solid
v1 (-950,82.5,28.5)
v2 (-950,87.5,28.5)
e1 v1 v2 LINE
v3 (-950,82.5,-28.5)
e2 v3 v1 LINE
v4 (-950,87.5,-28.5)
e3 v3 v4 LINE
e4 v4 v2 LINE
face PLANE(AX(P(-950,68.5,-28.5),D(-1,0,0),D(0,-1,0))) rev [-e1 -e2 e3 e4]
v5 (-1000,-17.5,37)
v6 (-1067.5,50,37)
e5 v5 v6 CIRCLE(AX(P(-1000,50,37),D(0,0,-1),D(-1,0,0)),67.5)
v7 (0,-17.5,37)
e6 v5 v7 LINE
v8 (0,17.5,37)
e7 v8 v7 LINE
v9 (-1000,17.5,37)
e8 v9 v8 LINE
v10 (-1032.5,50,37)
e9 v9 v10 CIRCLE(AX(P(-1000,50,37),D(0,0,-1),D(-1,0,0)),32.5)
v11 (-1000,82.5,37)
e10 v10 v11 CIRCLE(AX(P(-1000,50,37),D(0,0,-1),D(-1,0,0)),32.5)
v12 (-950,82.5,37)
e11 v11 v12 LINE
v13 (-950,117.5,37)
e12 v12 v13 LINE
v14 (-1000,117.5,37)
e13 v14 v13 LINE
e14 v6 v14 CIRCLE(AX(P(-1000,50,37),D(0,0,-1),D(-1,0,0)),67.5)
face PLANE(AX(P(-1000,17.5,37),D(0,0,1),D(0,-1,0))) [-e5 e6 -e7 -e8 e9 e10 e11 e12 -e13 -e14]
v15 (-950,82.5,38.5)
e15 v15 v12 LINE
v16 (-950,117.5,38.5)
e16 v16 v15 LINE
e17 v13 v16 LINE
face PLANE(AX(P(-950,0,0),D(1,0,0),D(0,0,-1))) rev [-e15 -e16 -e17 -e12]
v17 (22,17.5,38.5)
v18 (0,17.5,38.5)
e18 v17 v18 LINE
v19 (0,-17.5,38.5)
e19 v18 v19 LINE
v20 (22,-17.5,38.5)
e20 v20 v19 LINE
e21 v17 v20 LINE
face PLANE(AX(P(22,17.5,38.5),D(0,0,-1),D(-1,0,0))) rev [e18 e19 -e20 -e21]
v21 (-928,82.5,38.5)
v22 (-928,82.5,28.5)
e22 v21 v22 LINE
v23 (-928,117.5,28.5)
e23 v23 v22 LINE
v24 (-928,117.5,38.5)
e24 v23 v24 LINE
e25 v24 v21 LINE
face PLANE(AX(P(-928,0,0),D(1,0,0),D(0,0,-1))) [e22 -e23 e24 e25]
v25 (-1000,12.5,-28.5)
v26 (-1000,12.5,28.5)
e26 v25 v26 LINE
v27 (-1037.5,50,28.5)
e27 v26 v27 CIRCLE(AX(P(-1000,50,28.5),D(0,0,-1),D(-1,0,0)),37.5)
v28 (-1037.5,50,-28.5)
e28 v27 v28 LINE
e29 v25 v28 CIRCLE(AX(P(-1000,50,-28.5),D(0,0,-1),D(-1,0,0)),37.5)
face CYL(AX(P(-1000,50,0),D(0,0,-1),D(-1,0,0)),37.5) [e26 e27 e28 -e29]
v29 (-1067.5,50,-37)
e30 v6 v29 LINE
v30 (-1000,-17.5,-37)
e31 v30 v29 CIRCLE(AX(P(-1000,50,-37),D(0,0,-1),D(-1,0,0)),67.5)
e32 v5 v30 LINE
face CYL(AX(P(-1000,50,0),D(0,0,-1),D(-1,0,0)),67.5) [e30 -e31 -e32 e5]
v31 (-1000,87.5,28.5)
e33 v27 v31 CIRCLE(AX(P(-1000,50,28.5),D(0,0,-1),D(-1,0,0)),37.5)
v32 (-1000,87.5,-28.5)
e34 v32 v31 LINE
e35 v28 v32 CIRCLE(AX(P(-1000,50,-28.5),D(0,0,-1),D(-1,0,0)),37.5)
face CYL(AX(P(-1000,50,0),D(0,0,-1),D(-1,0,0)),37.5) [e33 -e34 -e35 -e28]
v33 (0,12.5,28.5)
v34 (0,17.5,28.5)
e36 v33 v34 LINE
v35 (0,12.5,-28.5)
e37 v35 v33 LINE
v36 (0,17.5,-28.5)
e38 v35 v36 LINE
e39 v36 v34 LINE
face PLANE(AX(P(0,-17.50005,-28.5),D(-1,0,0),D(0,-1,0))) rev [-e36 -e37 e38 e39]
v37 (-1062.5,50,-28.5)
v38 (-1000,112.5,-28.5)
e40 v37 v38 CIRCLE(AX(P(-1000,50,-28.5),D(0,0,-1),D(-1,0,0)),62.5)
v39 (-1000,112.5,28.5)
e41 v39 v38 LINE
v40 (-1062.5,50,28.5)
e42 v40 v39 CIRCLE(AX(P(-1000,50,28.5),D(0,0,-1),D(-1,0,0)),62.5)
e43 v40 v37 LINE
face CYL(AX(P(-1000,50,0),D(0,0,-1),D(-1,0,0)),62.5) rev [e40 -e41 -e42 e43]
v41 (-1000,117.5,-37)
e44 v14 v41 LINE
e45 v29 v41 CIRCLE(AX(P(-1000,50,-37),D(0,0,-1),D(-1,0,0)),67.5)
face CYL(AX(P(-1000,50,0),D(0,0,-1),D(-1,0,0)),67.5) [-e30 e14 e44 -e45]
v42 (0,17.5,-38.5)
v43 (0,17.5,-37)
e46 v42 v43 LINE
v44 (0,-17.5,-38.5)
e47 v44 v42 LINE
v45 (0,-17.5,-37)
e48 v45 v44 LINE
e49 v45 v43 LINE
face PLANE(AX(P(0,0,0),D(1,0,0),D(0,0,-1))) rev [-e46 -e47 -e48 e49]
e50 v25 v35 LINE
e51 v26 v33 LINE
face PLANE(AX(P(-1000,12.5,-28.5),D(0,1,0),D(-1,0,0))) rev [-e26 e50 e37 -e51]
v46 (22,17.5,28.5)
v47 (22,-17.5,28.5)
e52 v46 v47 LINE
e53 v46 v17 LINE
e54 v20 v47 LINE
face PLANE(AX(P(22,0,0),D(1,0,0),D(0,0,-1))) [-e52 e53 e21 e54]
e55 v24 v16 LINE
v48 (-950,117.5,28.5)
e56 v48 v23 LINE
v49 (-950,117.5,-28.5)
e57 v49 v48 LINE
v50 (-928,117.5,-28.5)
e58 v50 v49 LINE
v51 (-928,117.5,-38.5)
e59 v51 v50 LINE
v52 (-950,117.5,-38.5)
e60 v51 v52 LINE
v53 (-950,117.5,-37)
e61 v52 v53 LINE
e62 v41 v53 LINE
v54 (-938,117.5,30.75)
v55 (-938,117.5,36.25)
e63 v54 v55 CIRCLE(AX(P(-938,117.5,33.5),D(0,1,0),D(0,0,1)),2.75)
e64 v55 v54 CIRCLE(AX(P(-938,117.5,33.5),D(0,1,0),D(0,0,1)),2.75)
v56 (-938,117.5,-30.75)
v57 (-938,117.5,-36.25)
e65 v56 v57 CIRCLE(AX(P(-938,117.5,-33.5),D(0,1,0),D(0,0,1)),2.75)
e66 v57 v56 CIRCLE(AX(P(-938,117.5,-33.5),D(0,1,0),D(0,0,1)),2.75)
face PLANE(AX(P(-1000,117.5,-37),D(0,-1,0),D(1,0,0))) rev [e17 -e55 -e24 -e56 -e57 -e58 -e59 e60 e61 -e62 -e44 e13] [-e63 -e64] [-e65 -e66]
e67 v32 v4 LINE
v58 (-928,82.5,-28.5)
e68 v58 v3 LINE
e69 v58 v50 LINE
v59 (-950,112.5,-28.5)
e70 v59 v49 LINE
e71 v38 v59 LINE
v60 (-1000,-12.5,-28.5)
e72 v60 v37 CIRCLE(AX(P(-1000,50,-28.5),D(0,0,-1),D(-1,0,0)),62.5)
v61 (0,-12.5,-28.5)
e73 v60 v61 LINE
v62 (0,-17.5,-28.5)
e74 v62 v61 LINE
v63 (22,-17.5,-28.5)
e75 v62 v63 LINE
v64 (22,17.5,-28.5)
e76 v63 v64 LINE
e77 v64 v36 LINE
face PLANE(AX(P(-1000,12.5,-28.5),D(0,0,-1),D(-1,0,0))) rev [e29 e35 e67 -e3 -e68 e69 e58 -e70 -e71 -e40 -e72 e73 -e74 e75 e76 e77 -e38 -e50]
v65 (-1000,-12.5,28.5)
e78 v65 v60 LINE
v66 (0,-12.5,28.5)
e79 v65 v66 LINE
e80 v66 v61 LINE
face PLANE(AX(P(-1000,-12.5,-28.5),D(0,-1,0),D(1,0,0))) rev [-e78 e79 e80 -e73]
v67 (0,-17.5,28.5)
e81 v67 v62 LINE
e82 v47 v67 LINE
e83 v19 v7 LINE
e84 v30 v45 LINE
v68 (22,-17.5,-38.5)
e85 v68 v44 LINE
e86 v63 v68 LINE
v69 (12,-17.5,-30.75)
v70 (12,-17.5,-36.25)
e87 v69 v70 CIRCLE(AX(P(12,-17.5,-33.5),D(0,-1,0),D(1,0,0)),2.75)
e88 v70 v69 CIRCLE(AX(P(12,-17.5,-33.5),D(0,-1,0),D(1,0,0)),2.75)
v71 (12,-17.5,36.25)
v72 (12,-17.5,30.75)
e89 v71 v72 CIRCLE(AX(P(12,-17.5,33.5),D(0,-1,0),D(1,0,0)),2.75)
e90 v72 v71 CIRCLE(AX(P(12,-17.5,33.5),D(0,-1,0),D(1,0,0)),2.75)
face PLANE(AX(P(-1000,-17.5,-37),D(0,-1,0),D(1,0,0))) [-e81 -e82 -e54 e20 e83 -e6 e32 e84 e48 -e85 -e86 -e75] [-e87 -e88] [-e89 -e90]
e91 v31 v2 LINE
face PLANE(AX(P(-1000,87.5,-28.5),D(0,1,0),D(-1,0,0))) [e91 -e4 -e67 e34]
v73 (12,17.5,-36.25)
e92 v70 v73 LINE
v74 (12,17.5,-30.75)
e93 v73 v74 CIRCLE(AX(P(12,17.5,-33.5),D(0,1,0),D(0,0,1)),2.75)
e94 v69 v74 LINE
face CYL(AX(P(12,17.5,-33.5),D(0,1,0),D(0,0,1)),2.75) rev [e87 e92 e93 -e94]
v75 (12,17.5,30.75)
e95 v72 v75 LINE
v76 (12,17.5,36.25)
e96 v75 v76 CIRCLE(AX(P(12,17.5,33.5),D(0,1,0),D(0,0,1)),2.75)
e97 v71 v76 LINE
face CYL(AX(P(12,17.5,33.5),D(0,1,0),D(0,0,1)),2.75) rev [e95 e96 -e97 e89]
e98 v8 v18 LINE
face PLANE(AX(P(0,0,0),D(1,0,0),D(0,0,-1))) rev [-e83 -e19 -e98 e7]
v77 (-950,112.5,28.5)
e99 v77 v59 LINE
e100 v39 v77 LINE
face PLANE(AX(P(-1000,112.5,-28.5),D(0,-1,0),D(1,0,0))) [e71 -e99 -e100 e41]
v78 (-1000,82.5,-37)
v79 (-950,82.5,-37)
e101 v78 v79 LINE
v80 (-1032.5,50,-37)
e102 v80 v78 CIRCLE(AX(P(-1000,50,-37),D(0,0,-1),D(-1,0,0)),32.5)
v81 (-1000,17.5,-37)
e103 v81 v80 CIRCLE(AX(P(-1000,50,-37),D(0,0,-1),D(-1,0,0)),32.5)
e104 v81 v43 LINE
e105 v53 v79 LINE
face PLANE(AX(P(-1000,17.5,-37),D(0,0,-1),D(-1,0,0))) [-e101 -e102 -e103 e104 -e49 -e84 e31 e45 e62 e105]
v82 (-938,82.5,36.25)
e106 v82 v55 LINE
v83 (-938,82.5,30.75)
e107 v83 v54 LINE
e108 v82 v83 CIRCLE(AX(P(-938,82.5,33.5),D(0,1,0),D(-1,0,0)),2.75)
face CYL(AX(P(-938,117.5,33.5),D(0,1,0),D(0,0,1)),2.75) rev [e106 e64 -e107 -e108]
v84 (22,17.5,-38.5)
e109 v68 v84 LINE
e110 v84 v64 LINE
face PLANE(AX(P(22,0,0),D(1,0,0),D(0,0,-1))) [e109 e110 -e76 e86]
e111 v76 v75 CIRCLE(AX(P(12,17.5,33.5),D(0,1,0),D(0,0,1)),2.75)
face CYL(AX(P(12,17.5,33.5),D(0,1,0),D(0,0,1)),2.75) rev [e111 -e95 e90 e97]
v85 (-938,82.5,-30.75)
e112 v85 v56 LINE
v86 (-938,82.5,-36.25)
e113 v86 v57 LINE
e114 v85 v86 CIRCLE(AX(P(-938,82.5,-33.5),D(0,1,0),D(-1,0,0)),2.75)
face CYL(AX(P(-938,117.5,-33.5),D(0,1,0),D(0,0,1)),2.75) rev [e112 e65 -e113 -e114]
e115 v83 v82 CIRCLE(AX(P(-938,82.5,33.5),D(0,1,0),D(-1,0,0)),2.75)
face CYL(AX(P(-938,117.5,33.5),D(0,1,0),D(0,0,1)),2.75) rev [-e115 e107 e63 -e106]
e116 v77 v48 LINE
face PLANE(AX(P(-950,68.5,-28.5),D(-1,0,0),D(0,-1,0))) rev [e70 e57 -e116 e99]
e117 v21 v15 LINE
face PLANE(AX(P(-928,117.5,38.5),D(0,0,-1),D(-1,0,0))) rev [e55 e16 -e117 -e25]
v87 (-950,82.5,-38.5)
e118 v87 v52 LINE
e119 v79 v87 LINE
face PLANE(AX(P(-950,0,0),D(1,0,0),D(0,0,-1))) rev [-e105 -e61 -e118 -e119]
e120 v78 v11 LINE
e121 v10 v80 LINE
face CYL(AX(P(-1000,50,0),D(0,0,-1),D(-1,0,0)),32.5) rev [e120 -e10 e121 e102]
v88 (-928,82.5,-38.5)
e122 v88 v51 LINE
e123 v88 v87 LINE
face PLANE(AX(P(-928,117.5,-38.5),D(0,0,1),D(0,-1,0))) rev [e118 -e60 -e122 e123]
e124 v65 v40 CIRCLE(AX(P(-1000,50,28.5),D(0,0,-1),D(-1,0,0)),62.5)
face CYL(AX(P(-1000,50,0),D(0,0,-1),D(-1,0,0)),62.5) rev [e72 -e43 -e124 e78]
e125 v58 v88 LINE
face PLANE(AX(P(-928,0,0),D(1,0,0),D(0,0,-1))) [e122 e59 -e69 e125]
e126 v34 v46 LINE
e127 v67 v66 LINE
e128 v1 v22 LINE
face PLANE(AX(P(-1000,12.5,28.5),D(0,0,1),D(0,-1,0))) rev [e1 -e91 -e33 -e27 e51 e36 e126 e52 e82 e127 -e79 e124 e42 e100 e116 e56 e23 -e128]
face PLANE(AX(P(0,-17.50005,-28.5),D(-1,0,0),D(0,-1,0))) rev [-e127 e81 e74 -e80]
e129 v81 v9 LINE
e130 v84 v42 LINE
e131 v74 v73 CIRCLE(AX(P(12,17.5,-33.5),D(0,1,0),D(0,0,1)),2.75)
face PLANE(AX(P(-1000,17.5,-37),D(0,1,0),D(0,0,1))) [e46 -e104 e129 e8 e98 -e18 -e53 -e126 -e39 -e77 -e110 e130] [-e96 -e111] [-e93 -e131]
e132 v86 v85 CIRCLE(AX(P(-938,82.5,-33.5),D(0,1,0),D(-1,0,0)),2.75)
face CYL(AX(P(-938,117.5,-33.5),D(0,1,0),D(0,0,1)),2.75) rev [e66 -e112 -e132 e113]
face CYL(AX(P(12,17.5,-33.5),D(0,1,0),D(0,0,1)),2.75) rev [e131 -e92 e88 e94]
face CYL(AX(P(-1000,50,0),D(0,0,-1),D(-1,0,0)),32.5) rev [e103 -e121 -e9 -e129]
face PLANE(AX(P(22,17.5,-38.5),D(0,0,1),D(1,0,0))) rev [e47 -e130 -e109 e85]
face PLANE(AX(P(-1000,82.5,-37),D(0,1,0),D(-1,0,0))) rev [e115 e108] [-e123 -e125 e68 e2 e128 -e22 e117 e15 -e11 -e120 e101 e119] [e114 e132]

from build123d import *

# Parameters (mm, degrees)
SKETCH_2_W                  = 74
SKETCH_2_H                  = 35
SKETCH_2_W_2                = 57
SKETCH_2_H_2                = 25
SKETCH_11_W                 = 77
SKETCH_11_H                 = 35
SKETCH_11_W_2               = 57
SKETCH_11_H_2               = 25
EXTRUDE_1_DEPTH             = 22
SKETCH_12_W                 = 23.011901601
SKETCH_12_H                 = 57
CUT_EXTRUDE_9_DEPTH         = 1073.864623333
HOLE_WIZARD_5_5_5_5_1_D     = 5.5
SKETCH_15_W                 = 77
SKETCH_15_H                 = 35
SKETCH_15_W_2               = 57
SKETCH_15_H_2               = 25
EXTRUDE_2_DEPTH             = 22
SKETCH_16_W                 = 45.795478168
SKETCH_16_H                 = 57
CUT_EXTRUDE_10_DEPTH        = 49
HOLE_WIZARD_5_5_5_5_2_D     = 5.5
HOLE_WIZARD_5_5_5_5_2_DEPTH = 50
HOLE_WIZARD_5_5_5_5_2_TIP   = 1.652366702


with BuildPart() as part:
    # 扫描1: sweep along a path in 草图1
    with BuildLine(Plane.XY) as sweep_1_path:
        Line((0, 0), (-1000, 0))
        ThreePointArc((-1000, 0), (-1050, 50), (-1000, 100))
        Line((-1000, 100), (-950, 100))
    # 草图2 → 扫描1 (sweep)
    with BuildSketch(Plane(origin=(0, 0, 0), x_dir=(0, 0, -1), z_dir=(1, 0, 0))):
        Rectangle(SKETCH_2_W, SKETCH_2_H)
        Rectangle(SKETCH_2_W_2, SKETCH_2_H_2, mode=Mode.SUBTRACT)
    sweep(path=sweep_1_path.line)

    # 草图11 → 凸台-拉伸1 (add)
    with BuildSketch(Plane(origin=(0, 0, 0), x_dir=(0, 0, -1), z_dir=(1, 0, 0))):
        Rectangle(SKETCH_11_W, SKETCH_11_H)
        Rectangle(SKETCH_11_W_2, SKETCH_11_H_2, mode=Mode.SUBTRACT)
    extrude(amount=EXTRUDE_1_DEPTH)

    # 草图12 → 切除-拉伸9 (cut, through all)
    with BuildSketch(Plane(origin=(0, 17.5, 0), x_dir=(1, 0, 0), z_dir=(0, 1, 0))):
        with Locations((11.505950801, 0)):
            Rectangle(SKETCH_12_W, SKETCH_12_H)
    extrude(amount=-CUT_EXTRUDE_9_DEPTH, mode=Mode.SUBTRACT)

    # Ø5.5 (5.5) 直径孔1 (through all)
    with Locations(Plane(origin=(0, 17.5, 0), x_dir=(1, 0, 0), z_dir=(0, 1, 0))):
        with Locations((12, 33.5), (12, -33.5)):
            Hole(HOLE_WIZARD_5_5_5_5_1_D / 2)

    # 草图15 → 凸台-拉伸2 (add)
    with BuildSketch(Plane(origin=(-950, 0, 0), x_dir=(0, 0, -1), z_dir=(1, 0, 0))):
        with Locations((0, 100)):
            Rectangle(SKETCH_15_W, SKETCH_15_H)
        with Locations((0, 100)):
            Rectangle(SKETCH_15_W_2, SKETCH_15_H_2, mode=Mode.SUBTRACT)
    extrude(amount=EXTRUDE_2_DEPTH)

    # 草图16 → 切除-拉伸10 (cut)
    with BuildSketch(Plane(origin=(0, 117.5, 0), x_dir=(1, 0, 0), z_dir=(0, 1, 0))):
        with Locations((-927.102260916, 0)):
            Rectangle(SKETCH_16_W, SKETCH_16_H)
    extrude(amount=-CUT_EXTRUDE_10_DEPTH, mode=Mode.SUBTRACT)

    # Ø5.5 (5.5) 直径孔2
    with Locations(Plane(origin=(0, 117.5, 0), x_dir=(1, 0, 0), z_dir=(0, 1, 0))):
        with Locations((-938, 33.5), (-938, -33.5)):
            Hole(HOLE_WIZARD_5_5_5_5_2_D / 2, depth=HOLE_WIZARD_5_5_5_5_2_DEPTH)
            with Locations((0, 0, -(HOLE_WIZARD_5_5_5_5_2_DEPTH + HOLE_WIZARD_5_5_5_5_2_TIP / 2))):  # 118° drill point
                Cone(0, HOLE_WIZARD_5_5_5_5_2_D / 2, HOLE_WIZARD_5_5_5_5_2_TIP, mode=Mode.SUBTRACT)


solid = part.part
